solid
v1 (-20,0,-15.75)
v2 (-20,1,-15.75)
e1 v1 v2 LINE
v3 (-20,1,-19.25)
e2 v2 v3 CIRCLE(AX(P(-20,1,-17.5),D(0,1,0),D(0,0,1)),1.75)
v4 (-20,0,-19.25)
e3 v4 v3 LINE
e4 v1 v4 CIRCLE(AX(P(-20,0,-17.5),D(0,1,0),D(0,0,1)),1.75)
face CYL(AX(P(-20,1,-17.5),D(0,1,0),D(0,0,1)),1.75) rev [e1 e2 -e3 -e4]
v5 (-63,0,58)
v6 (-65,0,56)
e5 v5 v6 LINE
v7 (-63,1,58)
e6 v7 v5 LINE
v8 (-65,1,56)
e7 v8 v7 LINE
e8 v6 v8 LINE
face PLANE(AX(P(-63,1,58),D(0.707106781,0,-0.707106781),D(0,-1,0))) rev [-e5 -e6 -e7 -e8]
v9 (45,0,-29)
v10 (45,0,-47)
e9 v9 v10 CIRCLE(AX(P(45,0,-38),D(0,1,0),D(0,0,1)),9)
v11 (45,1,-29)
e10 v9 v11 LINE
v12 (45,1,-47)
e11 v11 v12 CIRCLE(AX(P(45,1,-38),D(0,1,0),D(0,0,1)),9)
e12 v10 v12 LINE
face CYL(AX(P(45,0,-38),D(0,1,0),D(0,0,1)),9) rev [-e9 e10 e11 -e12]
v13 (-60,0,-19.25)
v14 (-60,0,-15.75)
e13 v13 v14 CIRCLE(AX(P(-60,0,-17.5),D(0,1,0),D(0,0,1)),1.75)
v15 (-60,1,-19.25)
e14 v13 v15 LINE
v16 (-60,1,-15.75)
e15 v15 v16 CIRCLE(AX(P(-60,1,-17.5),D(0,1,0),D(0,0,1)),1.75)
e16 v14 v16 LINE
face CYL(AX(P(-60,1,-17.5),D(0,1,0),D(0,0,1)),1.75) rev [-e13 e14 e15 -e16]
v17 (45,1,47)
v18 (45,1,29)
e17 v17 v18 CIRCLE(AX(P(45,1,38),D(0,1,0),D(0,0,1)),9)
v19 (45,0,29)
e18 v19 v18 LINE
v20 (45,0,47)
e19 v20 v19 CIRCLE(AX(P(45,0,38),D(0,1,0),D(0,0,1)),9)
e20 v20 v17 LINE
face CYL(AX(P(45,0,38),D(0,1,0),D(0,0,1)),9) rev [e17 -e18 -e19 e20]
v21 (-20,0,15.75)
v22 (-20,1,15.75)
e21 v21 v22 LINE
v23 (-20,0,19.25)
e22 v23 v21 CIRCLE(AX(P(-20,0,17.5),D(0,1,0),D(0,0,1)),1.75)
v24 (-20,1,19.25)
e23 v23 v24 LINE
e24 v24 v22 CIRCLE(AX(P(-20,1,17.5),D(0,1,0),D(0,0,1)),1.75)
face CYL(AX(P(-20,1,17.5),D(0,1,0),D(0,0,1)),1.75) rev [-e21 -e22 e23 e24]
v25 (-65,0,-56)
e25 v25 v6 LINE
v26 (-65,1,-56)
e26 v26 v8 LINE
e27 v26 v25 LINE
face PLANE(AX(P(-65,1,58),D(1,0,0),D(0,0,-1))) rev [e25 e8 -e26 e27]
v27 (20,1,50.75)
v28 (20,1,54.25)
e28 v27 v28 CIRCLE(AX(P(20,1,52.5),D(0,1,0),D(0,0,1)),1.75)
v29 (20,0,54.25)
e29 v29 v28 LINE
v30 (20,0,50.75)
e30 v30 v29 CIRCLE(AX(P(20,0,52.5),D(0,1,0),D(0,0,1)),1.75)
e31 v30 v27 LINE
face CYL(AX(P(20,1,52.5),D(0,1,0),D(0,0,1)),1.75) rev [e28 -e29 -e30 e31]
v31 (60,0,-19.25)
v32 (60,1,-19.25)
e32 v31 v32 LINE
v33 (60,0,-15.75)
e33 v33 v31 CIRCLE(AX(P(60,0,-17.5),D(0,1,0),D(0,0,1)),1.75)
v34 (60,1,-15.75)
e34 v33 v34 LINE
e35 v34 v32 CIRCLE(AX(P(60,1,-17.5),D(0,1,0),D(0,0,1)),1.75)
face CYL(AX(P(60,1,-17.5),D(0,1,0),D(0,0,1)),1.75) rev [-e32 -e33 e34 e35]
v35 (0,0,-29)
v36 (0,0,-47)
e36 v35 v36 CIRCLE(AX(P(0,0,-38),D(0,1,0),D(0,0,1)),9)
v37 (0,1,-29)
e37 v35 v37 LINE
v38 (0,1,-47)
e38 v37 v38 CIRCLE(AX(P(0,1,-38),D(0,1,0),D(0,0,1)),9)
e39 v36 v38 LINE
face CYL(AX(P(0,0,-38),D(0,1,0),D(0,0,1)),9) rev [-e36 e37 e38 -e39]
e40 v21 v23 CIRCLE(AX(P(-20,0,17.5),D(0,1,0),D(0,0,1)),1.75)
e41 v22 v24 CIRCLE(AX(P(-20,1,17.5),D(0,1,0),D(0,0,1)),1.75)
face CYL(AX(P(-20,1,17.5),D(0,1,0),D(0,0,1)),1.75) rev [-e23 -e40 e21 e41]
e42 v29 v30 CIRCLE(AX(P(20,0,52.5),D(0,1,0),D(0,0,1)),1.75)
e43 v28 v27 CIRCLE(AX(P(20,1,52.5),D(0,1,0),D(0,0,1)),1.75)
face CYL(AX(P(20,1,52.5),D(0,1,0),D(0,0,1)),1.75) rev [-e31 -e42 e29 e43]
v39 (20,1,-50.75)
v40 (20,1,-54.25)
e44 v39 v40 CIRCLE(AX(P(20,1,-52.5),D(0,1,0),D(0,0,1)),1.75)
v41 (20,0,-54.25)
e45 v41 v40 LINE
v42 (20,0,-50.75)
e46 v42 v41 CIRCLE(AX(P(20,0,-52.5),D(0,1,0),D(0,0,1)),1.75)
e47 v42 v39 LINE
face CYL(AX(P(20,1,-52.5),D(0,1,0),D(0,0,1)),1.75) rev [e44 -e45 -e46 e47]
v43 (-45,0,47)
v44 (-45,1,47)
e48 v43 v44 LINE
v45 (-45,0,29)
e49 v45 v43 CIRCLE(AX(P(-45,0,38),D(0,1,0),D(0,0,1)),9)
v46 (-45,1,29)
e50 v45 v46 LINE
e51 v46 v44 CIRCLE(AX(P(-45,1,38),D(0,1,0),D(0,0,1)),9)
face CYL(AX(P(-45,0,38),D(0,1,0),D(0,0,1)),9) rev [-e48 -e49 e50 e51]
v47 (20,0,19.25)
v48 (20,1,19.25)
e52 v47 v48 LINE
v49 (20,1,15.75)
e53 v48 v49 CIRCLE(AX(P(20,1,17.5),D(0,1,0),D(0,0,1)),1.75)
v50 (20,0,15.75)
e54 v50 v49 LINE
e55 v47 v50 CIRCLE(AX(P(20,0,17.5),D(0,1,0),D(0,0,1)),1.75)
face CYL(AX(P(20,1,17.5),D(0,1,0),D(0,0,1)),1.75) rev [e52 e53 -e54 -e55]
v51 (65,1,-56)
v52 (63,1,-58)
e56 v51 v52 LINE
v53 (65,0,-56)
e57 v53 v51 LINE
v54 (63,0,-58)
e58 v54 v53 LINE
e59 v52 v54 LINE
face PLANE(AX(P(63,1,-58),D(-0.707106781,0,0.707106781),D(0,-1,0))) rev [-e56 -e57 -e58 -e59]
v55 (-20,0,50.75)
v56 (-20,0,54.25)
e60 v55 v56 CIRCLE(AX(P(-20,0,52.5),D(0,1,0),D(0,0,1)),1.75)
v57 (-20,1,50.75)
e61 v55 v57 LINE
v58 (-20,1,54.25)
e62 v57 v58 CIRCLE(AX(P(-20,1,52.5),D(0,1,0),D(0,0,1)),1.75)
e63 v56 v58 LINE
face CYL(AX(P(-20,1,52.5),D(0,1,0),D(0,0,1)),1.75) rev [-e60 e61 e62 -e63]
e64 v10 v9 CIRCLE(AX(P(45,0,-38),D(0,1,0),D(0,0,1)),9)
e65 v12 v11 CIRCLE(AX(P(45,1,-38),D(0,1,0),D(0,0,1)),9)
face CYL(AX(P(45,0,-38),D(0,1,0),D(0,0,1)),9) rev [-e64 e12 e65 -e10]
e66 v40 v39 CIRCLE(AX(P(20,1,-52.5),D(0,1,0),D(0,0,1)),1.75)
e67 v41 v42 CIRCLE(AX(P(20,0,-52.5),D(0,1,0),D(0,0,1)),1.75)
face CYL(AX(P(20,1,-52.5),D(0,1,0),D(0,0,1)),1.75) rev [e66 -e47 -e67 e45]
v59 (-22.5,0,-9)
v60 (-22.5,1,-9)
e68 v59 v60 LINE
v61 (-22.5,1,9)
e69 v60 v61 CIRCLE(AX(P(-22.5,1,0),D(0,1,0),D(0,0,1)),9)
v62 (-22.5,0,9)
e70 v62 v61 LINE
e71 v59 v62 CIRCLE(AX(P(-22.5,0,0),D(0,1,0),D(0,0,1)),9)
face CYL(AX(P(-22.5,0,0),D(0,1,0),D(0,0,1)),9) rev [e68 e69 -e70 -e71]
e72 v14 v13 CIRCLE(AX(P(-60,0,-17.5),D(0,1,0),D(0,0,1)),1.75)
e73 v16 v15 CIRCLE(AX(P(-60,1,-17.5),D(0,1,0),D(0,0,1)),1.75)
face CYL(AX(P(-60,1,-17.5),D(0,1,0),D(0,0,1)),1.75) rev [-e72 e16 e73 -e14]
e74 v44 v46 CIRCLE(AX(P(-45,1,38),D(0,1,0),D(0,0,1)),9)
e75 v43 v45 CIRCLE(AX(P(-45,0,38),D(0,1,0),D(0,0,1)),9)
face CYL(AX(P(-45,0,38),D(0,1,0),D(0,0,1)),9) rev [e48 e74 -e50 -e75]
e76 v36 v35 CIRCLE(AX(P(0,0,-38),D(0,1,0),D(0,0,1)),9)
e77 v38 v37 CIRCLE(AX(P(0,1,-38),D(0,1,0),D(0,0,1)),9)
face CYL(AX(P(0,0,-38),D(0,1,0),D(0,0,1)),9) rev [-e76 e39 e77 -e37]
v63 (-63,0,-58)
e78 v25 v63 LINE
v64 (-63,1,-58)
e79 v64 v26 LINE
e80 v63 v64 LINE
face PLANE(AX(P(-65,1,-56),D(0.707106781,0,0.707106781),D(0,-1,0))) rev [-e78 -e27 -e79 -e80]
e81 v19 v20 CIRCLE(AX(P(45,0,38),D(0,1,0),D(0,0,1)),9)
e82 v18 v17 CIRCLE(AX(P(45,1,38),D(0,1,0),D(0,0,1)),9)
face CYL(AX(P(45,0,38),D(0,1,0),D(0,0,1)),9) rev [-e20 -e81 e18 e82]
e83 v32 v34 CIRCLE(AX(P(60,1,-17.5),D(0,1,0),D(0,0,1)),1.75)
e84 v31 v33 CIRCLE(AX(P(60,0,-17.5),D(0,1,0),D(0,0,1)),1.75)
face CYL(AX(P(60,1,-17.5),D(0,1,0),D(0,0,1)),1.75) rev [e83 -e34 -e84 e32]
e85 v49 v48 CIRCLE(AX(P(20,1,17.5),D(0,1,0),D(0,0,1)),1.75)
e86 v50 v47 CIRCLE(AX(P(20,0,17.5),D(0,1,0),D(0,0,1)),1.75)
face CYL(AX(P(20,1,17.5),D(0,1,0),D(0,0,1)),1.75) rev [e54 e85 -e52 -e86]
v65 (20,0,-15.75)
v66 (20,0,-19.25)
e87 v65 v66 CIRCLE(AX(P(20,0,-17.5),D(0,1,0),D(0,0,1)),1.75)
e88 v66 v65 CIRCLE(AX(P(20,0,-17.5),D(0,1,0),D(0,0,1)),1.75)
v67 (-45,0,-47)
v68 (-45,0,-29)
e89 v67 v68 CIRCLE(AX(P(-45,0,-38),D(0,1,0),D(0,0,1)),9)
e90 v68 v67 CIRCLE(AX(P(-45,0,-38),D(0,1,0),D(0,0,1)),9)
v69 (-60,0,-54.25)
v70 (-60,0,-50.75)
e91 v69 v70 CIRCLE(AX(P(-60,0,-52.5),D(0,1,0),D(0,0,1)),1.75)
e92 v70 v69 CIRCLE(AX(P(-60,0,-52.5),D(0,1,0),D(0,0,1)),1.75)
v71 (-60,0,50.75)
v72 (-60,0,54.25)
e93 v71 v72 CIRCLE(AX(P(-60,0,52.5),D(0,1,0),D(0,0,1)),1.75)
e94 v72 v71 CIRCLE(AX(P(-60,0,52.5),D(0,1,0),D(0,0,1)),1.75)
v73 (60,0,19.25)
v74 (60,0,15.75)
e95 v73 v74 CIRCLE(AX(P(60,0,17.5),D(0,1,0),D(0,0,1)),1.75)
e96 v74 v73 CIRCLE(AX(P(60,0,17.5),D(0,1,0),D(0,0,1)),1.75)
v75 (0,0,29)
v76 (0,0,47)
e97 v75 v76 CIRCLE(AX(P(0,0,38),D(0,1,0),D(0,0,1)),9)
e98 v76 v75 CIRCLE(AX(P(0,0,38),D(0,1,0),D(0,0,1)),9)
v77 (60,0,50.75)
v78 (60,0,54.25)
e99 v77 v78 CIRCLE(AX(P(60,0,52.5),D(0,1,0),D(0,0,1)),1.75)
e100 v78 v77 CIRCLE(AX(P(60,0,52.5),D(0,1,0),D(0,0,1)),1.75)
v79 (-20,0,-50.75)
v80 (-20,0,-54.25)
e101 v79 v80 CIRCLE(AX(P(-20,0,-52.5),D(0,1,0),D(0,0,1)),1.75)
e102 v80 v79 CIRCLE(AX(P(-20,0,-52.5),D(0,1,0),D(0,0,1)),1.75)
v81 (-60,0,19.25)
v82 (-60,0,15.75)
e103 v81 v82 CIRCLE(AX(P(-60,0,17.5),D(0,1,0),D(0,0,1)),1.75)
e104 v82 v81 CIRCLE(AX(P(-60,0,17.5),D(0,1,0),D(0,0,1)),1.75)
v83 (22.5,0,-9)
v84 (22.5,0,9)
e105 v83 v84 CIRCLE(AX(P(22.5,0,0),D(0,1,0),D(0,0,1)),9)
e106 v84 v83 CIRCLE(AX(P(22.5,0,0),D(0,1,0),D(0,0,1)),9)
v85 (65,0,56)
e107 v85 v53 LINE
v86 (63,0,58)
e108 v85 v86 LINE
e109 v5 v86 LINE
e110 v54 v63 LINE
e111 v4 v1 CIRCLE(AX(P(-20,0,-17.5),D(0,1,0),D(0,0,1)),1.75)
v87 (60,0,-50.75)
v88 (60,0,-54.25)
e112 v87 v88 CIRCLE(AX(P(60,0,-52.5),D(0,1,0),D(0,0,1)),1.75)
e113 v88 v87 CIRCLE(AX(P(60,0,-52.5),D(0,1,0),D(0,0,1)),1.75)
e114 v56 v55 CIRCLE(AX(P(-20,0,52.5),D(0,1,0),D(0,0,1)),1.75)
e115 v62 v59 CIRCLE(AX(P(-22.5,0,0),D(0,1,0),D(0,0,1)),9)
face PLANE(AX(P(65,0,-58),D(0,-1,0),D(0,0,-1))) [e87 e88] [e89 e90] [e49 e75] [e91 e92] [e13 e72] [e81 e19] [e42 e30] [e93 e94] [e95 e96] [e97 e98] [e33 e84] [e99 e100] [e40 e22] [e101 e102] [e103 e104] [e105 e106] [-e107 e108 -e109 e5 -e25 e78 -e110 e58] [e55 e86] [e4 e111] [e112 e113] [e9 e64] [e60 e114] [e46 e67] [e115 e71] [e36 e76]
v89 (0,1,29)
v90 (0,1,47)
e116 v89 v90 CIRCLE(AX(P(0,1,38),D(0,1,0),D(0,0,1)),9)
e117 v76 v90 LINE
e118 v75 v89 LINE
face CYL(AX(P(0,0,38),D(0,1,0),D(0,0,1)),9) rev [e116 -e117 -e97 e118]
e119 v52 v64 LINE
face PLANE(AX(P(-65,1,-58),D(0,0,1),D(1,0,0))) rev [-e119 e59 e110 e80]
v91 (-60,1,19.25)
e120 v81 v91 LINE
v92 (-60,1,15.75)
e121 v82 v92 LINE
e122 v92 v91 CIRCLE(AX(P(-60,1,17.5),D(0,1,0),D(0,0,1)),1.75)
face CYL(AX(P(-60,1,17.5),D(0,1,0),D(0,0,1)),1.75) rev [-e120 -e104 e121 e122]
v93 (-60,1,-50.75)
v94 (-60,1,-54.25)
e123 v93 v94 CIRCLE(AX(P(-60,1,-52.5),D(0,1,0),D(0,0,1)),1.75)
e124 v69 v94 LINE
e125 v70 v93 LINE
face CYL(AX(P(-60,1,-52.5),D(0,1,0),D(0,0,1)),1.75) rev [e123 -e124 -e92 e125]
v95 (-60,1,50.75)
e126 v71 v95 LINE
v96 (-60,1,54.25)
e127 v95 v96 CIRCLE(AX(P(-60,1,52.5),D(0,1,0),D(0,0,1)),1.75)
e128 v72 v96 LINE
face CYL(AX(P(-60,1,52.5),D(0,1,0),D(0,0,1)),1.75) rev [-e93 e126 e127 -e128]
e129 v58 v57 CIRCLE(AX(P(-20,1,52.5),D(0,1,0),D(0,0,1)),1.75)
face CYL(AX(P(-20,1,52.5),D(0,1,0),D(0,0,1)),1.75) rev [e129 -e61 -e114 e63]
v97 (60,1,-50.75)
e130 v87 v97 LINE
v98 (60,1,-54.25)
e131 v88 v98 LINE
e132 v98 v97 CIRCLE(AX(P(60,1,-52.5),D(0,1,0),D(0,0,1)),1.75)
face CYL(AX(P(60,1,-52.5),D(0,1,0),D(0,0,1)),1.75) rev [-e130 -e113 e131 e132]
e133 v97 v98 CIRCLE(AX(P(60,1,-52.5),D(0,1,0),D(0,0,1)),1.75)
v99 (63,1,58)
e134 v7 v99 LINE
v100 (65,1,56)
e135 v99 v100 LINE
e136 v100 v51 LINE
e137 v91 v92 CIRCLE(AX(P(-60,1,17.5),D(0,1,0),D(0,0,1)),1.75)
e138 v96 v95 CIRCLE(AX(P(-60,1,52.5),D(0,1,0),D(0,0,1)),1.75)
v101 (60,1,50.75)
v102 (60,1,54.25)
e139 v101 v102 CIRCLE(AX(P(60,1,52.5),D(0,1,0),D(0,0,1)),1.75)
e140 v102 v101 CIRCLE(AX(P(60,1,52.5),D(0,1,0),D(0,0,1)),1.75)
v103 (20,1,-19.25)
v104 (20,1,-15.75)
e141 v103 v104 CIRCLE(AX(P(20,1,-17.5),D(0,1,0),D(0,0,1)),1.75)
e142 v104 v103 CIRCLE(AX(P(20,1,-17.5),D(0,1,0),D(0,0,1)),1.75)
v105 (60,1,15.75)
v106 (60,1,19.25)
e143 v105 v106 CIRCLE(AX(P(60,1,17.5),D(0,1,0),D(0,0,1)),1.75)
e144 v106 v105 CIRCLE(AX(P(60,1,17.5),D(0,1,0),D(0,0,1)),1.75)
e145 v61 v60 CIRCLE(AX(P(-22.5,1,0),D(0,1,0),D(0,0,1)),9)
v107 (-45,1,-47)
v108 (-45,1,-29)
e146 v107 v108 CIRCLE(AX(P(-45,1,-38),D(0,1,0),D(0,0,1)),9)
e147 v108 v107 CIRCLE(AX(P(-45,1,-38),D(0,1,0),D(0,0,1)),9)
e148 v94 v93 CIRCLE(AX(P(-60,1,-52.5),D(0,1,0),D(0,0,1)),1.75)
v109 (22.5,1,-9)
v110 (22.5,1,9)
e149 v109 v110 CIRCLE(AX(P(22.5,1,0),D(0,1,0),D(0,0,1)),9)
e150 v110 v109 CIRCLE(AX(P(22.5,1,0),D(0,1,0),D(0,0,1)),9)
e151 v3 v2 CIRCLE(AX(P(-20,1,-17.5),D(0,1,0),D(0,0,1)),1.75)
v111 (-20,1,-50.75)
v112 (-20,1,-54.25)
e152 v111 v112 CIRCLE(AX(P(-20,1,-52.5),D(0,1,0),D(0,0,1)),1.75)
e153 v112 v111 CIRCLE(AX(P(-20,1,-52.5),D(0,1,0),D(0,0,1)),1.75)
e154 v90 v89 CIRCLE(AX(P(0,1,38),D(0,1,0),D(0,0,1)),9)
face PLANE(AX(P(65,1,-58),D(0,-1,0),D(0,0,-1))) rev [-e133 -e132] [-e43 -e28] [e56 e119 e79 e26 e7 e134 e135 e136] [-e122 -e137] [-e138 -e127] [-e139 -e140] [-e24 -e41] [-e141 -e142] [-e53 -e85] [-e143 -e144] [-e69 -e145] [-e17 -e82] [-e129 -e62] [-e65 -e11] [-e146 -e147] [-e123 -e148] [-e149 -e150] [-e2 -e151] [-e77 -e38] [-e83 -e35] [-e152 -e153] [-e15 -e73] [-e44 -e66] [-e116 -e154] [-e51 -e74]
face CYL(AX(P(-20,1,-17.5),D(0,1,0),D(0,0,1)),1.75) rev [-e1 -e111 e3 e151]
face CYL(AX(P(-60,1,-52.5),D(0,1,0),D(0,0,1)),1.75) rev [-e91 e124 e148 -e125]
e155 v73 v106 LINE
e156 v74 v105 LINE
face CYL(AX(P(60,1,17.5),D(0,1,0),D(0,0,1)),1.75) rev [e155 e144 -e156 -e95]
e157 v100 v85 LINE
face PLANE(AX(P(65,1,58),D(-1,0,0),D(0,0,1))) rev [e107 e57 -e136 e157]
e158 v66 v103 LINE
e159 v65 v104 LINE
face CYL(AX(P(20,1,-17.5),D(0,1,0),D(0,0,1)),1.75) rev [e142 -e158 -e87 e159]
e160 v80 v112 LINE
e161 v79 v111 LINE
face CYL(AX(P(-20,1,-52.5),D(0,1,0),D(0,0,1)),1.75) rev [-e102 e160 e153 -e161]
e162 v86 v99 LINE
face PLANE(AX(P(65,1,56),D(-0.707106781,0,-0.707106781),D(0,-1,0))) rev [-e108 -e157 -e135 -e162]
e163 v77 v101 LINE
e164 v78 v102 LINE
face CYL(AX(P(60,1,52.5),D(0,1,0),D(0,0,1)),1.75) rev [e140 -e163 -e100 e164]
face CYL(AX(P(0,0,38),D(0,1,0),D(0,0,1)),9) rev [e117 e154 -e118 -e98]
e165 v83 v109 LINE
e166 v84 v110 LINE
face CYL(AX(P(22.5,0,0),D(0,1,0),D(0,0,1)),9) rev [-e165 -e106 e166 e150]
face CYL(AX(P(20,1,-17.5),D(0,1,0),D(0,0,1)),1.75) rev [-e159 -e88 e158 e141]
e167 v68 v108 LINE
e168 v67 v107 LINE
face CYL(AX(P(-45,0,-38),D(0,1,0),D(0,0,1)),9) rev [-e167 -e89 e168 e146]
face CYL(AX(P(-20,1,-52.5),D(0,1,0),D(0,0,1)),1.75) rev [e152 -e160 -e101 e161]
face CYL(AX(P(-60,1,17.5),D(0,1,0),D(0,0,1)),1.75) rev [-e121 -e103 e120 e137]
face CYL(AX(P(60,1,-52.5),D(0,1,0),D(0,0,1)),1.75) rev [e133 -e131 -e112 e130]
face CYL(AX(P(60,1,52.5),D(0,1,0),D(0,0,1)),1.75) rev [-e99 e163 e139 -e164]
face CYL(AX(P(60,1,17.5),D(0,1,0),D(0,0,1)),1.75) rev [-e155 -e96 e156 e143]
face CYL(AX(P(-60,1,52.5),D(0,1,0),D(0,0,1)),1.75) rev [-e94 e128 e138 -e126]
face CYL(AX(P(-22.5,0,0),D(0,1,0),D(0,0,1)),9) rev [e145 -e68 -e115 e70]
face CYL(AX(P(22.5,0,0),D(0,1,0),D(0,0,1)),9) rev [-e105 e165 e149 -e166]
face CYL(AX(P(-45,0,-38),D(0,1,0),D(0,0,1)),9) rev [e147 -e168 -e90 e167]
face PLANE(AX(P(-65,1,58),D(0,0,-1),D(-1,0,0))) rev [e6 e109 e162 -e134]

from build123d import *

# Parameters (mm, degrees)
SKETCH1_W                  = 130
SKETCH1_H                  = 116
BOSS_EXTRUDE1_DEPTH        = 1
SKETCH2_R                  = 9
CUT_EXTRUDE1_DEPTH         = 88.120606058
LPATTERN1_COUNT            = 3
LPATTERN1_PITCH            = 38
LPATTERN1_COUNT_DIR2       = 5
LPATTERN1_PITCH_DIR2       = 22.5
CHAMFER1_SIZE              = 2
F_3_5_3_5_DIAMETER_HOLE1_D = 3.5
LPATTERN2_COUNT            = 4
LPATTERN2_PITCH            = 40
LPATTERN2_COUNT_DIR2       = 4
LPATTERN2_PITCH_DIR2       = 35


with BuildPart() as part:
    # Sketch1 → Boss-Extrude1 (new body)
    with BuildSketch(Plane(origin=(0, 0, 0), x_dir=(1, 0, 0), z_dir=(0, 1, 0))):
        Rectangle(SKETCH1_W, SKETCH1_H)
    extrude(amount=BOSS_EXTRUDE1_DEPTH)

    # Sketch2 → Cut-Extrude1 (cut, through all)
    with BuildSketch(Plane(origin=(0, 1, 0), x_dir=(1, 0, 0), z_dir=(0, 1, 0))):
        with Locations(Location((45, -38, 0), (0, 0, 270))):
            Circle(SKETCH2_R)
    cut_extrude1 = extrude(amount=-CUT_EXTRUDE1_DEPTH, mode=Mode.SUBTRACT)

    # LPattern1: Cut-Extrude1 3 × 5, 7 skipped
    with Locations(*[(-j * LPATTERN1_PITCH_DIR2, 0, -i * LPATTERN1_PITCH) for i in range(LPATTERN1_COUNT) for j in range(LPATTERN1_COUNT_DIR2) if (i, j) not in ((0, 0), (0, 1), (0, 3), (1, 0), (1, 2), (1, 4), (2, 1), (2, 3))]):
        add(cut_extrude1, mode=Mode.SUBTRACT)

    # Chamfer1
    chamfer1_edges = [part.edges().sort_by_distance(p)[0] for p in [
        (65, 0.5, 58),
        (-65, 0.5, 58),
        (-65, 0.5, -58),
        (65, 0.5, -58),
    ]]
    chamfer(chamfer1_edges, length=CHAMFER1_SIZE)

    # Ø3.5 (3.5) Diameter Hole1 (through all)
    with Locations(Plane(origin=(0, 1, 0), x_dir=(1, 0, 0), z_dir=(0, 1, 0))):
        with Locations((60, -52.5)):
            f_3_5_3_5_diameter_hole1 = Hole(F_3_5_3_5_DIAMETER_HOLE1_D / 2)

    # LPattern2: 3.5 _3.5_ Diameter Hole1 4 × 4
    with Locations(*[(-i * LPATTERN2_PITCH, 0, -j * LPATTERN2_PITCH_DIR2) for i in range(LPATTERN2_COUNT) for j in range(LPATTERN2_COUNT_DIR2) if (i, j) != (0, 0)]):
        add(f_3_5_3_5_diameter_hole1, mode=Mode.SUBTRACT)


solid = part.part
